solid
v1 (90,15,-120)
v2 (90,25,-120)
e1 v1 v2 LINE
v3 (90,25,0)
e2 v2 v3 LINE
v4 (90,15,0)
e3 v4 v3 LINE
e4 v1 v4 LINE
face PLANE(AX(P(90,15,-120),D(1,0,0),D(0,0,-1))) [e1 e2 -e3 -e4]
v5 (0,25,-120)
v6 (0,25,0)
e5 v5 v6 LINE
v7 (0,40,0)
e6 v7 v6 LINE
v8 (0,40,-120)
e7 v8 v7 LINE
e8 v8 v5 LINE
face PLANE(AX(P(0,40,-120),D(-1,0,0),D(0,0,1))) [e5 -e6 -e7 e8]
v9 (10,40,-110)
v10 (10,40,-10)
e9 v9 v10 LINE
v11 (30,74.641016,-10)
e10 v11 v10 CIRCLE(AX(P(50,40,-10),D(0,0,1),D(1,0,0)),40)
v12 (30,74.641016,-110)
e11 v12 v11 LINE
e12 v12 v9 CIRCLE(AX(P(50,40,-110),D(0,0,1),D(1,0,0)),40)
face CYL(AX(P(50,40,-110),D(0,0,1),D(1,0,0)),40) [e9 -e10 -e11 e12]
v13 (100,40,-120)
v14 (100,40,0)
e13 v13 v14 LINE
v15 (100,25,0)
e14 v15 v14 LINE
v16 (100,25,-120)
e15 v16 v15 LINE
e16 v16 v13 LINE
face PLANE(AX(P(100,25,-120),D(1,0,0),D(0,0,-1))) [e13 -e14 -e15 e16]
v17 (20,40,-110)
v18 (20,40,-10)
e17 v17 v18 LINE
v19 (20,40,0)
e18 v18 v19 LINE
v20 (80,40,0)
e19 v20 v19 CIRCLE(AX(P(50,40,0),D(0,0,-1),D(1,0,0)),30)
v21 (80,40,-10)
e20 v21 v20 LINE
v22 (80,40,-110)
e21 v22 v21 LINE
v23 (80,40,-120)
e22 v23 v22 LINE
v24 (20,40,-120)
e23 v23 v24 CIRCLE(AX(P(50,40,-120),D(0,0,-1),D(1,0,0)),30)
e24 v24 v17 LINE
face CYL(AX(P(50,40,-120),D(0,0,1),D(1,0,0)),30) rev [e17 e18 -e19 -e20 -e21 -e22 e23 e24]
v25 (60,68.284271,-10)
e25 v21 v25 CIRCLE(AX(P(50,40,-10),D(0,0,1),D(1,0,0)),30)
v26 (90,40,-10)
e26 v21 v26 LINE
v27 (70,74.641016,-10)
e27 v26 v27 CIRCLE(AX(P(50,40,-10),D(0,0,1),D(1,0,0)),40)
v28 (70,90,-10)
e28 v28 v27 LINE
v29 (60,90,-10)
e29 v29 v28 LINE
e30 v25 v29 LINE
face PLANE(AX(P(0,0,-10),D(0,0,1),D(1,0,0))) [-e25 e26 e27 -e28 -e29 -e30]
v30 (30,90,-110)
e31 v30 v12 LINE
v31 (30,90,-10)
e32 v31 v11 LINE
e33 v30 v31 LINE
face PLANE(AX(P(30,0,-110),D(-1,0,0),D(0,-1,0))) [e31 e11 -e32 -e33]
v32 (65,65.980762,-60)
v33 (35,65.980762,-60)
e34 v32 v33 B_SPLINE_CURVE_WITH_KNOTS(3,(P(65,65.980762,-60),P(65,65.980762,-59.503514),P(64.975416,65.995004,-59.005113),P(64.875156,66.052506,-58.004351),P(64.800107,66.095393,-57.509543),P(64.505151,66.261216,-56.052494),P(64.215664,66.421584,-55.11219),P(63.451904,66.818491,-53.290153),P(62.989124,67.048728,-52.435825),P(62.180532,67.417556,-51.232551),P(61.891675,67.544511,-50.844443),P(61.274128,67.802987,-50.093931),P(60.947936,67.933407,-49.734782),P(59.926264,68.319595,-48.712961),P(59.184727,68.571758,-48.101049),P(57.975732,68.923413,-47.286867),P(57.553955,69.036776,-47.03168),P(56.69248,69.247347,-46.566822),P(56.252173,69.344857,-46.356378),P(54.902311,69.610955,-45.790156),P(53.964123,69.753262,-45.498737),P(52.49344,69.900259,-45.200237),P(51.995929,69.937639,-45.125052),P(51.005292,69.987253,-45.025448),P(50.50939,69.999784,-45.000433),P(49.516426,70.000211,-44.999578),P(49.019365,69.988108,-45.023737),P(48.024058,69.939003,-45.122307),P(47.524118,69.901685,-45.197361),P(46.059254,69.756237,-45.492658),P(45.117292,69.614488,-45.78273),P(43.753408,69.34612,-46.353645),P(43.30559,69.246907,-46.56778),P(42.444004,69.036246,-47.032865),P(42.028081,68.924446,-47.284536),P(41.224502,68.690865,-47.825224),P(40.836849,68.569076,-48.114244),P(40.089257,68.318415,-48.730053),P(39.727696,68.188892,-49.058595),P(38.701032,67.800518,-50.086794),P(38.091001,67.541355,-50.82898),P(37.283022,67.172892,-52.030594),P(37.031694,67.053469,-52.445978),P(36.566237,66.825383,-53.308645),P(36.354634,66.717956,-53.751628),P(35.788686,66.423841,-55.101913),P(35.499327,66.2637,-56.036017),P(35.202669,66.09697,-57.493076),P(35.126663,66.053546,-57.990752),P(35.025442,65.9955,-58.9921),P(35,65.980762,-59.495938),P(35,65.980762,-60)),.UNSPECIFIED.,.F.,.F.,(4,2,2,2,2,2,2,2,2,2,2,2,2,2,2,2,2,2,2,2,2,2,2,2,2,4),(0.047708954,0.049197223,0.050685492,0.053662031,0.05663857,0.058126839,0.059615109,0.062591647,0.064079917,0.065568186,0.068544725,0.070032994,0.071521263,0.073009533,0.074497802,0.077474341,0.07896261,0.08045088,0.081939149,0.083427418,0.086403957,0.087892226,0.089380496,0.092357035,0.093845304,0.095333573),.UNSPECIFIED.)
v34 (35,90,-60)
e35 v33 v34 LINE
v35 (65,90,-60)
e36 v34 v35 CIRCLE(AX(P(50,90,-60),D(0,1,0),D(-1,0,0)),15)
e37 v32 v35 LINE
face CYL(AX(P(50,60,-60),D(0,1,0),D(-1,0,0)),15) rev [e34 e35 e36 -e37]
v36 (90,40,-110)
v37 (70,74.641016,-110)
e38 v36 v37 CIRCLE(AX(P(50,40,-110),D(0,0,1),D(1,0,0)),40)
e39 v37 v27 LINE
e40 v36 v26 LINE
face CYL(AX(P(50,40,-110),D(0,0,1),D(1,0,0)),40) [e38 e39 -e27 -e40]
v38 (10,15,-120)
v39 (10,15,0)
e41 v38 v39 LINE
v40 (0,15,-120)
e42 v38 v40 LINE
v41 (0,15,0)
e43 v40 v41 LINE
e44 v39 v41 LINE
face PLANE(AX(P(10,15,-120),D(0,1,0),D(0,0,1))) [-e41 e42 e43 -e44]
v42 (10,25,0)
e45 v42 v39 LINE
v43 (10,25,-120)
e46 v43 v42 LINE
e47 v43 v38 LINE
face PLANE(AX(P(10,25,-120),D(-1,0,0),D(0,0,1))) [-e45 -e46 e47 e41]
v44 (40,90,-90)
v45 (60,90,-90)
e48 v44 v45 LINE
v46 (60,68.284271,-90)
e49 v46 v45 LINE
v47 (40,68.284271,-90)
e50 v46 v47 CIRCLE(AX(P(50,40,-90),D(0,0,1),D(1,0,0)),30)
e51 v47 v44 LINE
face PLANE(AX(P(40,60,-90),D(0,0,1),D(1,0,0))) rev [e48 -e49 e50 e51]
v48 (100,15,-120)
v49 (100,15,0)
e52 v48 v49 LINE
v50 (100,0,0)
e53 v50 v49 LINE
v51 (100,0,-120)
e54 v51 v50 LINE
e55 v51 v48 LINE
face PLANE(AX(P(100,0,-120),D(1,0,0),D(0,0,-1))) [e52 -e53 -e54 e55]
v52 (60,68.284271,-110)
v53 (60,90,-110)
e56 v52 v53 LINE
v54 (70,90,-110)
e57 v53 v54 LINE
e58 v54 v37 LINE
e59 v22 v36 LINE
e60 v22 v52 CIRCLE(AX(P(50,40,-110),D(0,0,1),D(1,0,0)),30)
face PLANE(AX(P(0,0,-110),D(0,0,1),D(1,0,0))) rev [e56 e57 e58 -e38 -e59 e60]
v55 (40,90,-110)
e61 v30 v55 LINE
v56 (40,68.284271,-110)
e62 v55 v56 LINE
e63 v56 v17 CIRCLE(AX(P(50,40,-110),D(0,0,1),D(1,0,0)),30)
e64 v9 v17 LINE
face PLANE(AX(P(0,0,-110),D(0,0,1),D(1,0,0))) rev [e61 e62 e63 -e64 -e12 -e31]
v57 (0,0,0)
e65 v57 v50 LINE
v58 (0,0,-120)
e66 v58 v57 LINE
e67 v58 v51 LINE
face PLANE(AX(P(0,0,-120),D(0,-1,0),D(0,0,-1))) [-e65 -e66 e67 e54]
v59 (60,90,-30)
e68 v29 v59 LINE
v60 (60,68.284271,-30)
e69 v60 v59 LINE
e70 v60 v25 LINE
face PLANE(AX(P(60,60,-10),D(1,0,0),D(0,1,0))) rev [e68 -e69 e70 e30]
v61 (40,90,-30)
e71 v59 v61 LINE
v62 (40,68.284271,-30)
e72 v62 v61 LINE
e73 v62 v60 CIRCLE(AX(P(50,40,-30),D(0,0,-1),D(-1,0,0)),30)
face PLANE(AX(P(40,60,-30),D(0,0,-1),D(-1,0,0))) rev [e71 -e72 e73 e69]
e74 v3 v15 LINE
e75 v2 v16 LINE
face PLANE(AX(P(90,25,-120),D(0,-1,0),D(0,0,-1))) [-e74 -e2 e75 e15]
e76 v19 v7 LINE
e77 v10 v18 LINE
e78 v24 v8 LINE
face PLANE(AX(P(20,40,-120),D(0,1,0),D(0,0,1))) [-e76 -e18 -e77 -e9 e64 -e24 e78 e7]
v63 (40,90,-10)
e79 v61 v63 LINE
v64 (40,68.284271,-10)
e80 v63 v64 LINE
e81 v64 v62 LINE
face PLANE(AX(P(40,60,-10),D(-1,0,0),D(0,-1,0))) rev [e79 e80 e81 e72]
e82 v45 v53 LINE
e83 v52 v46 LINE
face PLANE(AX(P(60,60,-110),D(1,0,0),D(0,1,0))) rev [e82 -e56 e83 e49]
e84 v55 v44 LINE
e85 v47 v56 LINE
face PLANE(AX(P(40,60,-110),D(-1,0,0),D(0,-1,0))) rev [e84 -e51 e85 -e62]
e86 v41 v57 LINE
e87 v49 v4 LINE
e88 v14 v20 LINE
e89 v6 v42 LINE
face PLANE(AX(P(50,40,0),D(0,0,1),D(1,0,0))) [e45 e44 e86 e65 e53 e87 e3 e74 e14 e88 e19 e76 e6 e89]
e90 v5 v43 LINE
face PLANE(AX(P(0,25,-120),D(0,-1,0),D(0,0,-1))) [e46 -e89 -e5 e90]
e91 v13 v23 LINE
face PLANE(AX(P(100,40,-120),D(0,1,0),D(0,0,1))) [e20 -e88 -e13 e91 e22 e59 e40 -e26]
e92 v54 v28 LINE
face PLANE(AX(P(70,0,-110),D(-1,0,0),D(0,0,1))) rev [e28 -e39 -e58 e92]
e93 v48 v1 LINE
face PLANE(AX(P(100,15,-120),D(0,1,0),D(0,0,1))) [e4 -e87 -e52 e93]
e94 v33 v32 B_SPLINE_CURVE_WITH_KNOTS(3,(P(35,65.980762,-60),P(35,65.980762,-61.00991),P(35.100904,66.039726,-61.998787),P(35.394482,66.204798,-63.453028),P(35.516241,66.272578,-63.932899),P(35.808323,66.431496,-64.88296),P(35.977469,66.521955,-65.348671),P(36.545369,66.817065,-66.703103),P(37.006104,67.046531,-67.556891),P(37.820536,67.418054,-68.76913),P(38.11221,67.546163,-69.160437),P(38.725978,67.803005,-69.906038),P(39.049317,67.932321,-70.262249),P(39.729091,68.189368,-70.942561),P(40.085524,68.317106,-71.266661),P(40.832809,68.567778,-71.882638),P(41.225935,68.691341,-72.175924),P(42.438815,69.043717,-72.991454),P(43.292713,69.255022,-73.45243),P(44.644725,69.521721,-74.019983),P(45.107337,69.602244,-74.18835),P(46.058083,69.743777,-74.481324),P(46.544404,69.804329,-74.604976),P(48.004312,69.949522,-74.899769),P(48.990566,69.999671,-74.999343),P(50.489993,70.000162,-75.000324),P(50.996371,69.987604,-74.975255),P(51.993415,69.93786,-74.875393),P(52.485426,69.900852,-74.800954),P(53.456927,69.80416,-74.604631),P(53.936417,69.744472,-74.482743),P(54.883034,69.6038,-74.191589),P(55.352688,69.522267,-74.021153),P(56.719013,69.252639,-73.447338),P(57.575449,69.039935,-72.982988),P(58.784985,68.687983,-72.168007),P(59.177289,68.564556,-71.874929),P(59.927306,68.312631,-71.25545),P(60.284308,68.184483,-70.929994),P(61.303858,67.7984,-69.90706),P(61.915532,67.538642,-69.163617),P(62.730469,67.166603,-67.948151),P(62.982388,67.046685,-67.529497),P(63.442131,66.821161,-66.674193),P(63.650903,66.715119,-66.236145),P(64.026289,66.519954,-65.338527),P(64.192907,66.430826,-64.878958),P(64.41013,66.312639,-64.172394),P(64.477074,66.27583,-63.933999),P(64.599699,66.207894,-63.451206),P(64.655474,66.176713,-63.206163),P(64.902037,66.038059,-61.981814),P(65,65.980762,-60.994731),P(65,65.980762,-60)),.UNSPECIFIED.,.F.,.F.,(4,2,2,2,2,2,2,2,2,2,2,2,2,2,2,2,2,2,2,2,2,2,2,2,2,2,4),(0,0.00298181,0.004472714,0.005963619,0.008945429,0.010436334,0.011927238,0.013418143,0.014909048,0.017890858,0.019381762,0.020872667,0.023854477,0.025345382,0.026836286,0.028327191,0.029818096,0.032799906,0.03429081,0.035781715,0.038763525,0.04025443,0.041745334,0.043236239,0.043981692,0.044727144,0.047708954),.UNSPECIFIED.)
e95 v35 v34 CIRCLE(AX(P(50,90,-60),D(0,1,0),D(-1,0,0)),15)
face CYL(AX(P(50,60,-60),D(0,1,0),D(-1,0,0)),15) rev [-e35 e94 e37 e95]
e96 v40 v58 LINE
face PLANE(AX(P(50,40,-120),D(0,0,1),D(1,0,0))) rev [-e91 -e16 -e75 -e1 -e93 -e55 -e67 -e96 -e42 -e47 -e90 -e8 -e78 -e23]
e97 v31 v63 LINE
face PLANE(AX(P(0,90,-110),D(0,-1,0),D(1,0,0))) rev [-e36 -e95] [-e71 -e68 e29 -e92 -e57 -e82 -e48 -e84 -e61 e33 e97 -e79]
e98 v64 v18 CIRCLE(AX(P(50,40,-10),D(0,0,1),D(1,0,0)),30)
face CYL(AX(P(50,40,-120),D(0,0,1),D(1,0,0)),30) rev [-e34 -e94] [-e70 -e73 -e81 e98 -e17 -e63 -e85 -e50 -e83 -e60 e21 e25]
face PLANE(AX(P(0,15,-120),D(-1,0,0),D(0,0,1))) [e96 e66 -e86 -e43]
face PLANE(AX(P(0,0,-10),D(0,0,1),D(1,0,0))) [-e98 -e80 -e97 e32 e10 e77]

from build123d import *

# Parameters (mm, degrees)
BASE_BLOCK_DEPTH      = 120
BEARING_HOUSING_DEPTH = 100
TOP_SLOTS_SKETCH_W    = 20
TOP_SLOTS_SKETCH_H    = 20
TOP_SLOTS_DEPTH       = 30
TOP_HOLE_SKETCH_R     = 15
TOP_HOLE_30_DEPTH     = 30


with BuildPart() as part:
    # Base Profile Sketch → Base Block (new body)
    with BuildSketch(Plane.XY):
        with BuildLine():
            Line((0, 0), (100, 0))
            Line((100, 0), (100, 15))
            Line((100, 15), (90, 15))
            Line((90, 15), (90, 25))
            Line((90, 25), (100, 25))
            Line((100, 25), (100, 40))
            Line((100, 40), (80, 40))
            ThreePointArc((80, 40), (50, 10), (20, 40))
            Line((20, 40), (0, 40))
            Line((0, 40), (0, 25))
            Line((0, 25), (10, 25))
            Line((10, 25), (10, 15))
            Line((10, 15), (0, 15))
            Line((0, 15), (0, 0))
        make_face()
    extrude(amount=-BASE_BLOCK_DEPTH)

    # Bearing Housing Profile Sketch → Bearing Housing (add)
    with BuildSketch(Plane.XY.offset(-10)):
        with BuildLine():
            ThreePointArc((30, 74.641016151), (15.358983849, 60), (10, 40))
            Line((10, 40), (20, 40))
            ThreePointArc((20, 40), (50, 70), (80, 40))
            Line((80, 40), (90, 40))
            ThreePointArc((90, 40), (84.641016151, 60), (70, 74.641016151))
            ThreePointArc((70, 74.641016151), (50, 80), (30, 74.641016151))
        make_face()
        with BuildLine():
            Line((30, 90), (30, 74.641016151))
            ThreePointArc((30, 74.641016151), (50, 80), (70, 74.641016151))
            Line((70, 74.641016151), (70, 90))
            Line((70, 90), (30, 90))
        make_face()
    extrude(amount=-BEARING_HOUSING_DEPTH)

    # Top Slots Sketch → Top Slots (cut)
    with BuildSketch(Plane(origin=(0, 90, 0), x_dir=(1, 0, 0), z_dir=(0, 1, 0))):
        with Locations((50, 20)):
            Rectangle(TOP_SLOTS_SKETCH_W, TOP_SLOTS_SKETCH_H)
        with Locations((50, 100)):
            Rectangle(TOP_SLOTS_SKETCH_W, TOP_SLOTS_SKETCH_H)
    extrude(amount=-TOP_SLOTS_DEPTH, mode=Mode.SUBTRACT)

    # Top Hole Sketch → Top Hole Ø30 (cut)
    with BuildSketch(Plane(origin=(0, 90, 0), x_dir=(1, 0, 0), z_dir=(0, 1, 0))):
        with Locations(Location((50, 60, 0), (0, 0, 180))):
            Circle(TOP_HOLE_SKETCH_R)
    extrude(amount=-TOP_HOLE_30_DEPTH, mode=Mode.SUBTRACT)


solid = part.part
